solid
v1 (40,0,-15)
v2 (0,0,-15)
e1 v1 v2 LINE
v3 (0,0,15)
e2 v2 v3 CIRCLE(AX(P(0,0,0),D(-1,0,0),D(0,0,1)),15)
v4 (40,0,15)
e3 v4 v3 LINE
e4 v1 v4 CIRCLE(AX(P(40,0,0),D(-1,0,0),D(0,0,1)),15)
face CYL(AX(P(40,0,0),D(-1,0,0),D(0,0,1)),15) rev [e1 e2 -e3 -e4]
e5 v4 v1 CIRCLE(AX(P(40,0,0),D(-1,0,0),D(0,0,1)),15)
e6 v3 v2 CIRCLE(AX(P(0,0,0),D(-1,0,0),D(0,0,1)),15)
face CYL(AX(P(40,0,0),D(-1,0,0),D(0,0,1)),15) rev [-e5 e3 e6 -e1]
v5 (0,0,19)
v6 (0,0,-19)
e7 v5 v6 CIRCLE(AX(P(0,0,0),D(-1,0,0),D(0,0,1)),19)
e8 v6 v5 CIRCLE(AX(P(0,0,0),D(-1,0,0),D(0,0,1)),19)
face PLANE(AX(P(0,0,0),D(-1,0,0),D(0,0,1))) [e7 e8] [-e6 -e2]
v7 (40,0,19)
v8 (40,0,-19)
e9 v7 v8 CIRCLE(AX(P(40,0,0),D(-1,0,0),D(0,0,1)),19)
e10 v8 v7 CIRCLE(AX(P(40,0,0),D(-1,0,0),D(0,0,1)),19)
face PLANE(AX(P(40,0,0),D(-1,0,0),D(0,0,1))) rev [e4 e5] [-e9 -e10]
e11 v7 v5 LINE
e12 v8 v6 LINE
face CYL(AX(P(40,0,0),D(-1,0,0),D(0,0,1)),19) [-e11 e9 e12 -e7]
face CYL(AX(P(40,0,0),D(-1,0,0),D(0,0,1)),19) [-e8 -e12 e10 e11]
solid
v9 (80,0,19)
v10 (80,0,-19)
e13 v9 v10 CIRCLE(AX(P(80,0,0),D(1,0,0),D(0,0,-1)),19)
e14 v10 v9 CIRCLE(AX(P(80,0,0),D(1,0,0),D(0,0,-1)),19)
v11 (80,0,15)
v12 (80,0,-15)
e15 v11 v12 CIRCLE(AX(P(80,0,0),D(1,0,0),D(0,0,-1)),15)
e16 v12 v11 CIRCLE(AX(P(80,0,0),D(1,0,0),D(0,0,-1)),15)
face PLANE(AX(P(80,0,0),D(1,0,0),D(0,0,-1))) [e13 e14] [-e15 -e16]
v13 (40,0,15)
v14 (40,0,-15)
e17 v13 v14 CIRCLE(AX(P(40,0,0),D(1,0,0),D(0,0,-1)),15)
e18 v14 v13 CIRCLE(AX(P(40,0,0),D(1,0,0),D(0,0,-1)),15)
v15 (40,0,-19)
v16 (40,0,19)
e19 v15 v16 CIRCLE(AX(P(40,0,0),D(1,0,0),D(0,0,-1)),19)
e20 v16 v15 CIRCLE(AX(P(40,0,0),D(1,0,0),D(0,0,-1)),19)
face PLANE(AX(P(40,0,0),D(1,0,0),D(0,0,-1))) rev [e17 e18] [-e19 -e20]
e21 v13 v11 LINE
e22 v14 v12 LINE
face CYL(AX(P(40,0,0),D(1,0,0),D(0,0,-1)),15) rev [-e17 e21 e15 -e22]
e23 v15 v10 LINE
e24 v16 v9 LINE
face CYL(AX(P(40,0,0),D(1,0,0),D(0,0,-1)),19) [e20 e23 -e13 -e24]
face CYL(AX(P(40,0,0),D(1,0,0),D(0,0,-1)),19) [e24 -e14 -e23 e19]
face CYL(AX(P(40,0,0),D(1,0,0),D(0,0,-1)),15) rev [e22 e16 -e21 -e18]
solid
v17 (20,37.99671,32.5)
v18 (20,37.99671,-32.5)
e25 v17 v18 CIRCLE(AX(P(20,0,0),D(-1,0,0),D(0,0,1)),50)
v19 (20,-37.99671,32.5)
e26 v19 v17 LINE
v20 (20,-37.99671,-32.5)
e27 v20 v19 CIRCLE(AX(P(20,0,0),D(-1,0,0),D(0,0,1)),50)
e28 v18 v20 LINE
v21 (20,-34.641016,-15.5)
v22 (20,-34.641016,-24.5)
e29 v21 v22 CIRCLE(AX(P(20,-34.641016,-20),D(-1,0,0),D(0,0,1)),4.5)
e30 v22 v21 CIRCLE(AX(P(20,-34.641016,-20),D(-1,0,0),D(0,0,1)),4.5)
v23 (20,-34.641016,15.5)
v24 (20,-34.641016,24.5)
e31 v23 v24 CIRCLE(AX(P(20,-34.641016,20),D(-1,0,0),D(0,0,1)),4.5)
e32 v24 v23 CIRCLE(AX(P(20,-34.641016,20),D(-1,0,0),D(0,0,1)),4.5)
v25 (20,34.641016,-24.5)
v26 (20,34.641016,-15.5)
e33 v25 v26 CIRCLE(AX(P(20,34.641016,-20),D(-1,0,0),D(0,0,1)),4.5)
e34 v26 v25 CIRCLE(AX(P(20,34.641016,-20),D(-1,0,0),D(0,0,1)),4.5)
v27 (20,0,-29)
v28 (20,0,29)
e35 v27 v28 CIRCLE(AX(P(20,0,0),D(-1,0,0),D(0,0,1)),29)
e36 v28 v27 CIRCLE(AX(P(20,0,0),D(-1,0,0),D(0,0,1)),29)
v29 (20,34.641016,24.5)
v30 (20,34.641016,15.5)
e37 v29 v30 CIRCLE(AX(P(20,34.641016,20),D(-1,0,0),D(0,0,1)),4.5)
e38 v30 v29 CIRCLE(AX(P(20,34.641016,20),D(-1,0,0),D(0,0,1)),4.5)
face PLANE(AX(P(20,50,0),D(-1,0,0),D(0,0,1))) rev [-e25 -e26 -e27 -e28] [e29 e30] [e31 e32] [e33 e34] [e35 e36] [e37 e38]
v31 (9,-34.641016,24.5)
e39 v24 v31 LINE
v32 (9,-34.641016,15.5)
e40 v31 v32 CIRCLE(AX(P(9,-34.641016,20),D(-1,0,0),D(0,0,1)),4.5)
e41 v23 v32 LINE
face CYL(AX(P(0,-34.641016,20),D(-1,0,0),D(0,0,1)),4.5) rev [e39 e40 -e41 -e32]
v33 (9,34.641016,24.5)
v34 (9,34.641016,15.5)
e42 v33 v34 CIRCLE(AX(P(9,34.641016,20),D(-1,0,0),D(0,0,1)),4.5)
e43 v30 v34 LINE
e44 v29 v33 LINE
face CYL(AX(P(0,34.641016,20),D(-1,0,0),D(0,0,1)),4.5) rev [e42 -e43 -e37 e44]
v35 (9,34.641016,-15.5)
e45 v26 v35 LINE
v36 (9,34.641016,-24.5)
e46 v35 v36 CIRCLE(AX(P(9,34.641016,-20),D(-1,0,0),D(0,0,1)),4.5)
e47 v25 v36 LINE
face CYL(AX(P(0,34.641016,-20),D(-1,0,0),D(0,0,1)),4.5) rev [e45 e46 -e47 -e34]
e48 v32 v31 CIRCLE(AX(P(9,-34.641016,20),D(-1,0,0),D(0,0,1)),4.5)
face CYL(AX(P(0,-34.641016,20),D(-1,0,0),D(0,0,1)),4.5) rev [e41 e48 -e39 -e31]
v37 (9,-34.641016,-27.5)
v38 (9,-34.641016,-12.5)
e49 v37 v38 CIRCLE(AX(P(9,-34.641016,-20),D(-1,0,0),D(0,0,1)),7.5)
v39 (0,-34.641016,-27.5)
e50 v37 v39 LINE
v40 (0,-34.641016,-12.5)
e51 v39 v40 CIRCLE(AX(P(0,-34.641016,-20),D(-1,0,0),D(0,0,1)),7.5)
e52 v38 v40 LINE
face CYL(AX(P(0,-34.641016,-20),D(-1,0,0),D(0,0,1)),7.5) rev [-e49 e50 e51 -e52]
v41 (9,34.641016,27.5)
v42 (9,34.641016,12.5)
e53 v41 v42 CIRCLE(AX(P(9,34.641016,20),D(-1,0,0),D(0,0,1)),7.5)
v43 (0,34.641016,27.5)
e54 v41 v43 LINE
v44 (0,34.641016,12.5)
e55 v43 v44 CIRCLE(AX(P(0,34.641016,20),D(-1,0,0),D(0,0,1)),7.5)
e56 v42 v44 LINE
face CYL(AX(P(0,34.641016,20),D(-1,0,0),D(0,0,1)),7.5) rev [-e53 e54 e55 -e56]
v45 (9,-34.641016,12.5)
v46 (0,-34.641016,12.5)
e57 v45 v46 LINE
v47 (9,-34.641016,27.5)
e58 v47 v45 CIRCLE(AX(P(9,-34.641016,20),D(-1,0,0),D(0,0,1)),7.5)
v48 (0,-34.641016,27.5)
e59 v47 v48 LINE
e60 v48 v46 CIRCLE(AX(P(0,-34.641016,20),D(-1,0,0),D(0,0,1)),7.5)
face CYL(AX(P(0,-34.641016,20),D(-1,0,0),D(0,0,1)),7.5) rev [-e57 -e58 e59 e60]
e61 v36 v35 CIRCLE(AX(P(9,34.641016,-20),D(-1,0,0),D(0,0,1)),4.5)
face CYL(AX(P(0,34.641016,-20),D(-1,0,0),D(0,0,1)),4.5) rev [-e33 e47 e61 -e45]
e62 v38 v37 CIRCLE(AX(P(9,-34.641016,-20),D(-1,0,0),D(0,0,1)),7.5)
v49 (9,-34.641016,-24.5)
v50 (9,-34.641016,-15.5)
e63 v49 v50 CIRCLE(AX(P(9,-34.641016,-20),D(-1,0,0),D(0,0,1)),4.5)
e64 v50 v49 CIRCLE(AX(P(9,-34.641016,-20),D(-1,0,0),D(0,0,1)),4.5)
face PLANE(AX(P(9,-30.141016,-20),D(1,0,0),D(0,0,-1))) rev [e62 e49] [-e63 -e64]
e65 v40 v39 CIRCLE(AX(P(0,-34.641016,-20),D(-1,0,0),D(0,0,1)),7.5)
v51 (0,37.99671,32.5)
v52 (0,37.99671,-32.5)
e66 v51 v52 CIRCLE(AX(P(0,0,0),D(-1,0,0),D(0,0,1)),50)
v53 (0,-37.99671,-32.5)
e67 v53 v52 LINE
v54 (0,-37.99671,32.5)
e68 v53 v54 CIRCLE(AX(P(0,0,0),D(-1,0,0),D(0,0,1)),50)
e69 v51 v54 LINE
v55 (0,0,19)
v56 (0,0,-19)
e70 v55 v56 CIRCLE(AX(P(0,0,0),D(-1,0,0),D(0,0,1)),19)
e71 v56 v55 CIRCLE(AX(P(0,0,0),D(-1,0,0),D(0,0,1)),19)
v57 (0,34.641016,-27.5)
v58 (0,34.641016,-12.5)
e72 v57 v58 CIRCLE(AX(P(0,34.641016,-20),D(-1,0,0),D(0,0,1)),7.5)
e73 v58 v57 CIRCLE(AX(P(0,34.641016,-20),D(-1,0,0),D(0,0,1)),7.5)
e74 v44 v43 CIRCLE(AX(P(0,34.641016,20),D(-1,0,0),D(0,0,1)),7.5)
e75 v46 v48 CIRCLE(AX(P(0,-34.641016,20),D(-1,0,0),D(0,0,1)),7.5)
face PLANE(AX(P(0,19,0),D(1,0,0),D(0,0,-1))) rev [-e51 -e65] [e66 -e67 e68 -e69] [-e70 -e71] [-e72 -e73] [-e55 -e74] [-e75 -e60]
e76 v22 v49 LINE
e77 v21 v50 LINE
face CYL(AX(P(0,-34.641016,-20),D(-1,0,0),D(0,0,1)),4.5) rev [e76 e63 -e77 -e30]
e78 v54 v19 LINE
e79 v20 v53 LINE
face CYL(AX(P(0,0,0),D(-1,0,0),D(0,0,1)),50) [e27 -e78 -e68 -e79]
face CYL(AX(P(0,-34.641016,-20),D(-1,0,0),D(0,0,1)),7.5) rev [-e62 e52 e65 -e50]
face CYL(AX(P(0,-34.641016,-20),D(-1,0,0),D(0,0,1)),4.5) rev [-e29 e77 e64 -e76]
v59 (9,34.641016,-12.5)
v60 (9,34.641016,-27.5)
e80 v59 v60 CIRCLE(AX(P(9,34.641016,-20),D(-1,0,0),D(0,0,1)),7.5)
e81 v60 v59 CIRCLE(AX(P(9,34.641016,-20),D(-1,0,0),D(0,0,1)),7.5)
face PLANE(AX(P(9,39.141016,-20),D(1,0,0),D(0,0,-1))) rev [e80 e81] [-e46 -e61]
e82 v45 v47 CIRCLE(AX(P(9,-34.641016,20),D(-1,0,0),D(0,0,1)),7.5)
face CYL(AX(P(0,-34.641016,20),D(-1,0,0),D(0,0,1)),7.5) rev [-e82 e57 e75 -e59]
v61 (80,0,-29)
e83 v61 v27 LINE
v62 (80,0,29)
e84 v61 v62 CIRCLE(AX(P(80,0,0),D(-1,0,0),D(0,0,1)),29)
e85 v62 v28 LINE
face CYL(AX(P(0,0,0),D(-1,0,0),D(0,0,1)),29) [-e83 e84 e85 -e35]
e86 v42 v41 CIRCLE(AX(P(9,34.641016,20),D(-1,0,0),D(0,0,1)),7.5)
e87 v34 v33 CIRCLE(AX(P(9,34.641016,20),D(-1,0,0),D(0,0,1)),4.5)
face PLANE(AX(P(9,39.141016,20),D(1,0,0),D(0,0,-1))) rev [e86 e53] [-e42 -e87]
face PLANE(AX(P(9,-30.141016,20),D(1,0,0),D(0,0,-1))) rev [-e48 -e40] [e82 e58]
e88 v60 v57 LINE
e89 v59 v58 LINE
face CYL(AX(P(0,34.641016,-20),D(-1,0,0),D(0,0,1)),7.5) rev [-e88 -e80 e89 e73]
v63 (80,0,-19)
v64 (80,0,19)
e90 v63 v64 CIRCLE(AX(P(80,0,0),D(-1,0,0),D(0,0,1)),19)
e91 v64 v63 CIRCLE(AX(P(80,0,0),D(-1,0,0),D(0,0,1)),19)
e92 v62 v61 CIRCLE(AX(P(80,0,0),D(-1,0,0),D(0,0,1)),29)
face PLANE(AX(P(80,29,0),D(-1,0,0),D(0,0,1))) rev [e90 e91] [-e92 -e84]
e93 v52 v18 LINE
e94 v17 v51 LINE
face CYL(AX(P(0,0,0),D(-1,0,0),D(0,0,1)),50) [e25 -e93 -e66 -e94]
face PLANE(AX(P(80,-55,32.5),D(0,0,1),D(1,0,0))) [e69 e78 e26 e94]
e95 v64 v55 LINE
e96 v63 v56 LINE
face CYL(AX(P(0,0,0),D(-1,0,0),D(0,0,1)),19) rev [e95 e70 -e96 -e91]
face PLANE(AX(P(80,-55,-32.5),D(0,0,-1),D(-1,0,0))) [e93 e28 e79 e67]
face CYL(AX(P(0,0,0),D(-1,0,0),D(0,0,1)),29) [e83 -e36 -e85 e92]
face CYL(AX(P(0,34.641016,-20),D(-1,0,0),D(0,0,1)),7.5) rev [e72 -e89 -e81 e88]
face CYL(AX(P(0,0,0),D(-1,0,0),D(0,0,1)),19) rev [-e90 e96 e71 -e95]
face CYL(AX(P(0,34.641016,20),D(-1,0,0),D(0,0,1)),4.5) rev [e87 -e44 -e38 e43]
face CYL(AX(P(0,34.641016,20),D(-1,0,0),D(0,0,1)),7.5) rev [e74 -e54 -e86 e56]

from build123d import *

# Parameters (mm, degrees)
HOLE_SIZE_PER_SOCKET_HEAD_CAP_SCREW_TYPE_D           = 9
HOLE_SIZE_PER_SOCKET_HEAD_CAP_SCREW_TYPE_CBORE_D     = 15
HOLE_SIZE_PER_SOCKET_HEAD_CAP_SCREW_TYPE_CBORE_DEPTH = 9
SKETCH4_OUTSIDE_W                                    = 134.496
SKETCH4_OUTSIDE_H                                    = 134.496
SKETCH4_OUTSIDE_W_2                                  = 65
SKETCH4_OUTSIDE_H_2                                  = 110
CUT_EXTRUDE1_DEPTH                                   = 107.77078252
SKETCH5_R                                            = 19
SKETCH5_R_2                                          = 15
BOSS_EXTRUDE1_DEPTH                                  = 40
SKETCH6_R                                            = 19
SKETCH6_R_2                                          = 15
BOSS_EXTRUDE2_DEPTH                                  = 40


with BuildPart() as part:
    # Sketch1 → Revolve1 (revolve)
    with BuildSketch(Plane.XY, mode=Mode.PRIVATE) as revolve1_sk:
        Polygon((0, 19), (0, 50), (20, 50), (20, 29), (80, 29), (80, 19), align=None)
    revolve(revolve1_sk.sketch.rotate(Axis((0, 0, 0), (1, 0, 0)), 90), axis=Axis((0, 0, 0), (1, 0, 0)))

    # Hole size per socket head cap screw type1 (through all)
    with Locations(Plane.ZY):
        with Locations((20, 34.641016151), (-20, 34.641016151), (-20, -34.641016151), (20, -34.641016151)):
            CounterBoreHole(HOLE_SIZE_PER_SOCKET_HEAD_CAP_SCREW_TYPE_D / 2, HOLE_SIZE_PER_SOCKET_HEAD_CAP_SCREW_TYPE_CBORE_D / 2, HOLE_SIZE_PER_SOCKET_HEAD_CAP_SCREW_TYPE_CBORE_DEPTH)

    # Sketch4 outside → Cut-Extrude1 (cut, through all)
    with BuildSketch(Plane.ZY):
        Rectangle(SKETCH4_OUTSIDE_W, SKETCH4_OUTSIDE_H)
        Rectangle(SKETCH4_OUTSIDE_W_2, SKETCH4_OUTSIDE_H_2, mode=Mode.SUBTRACT)
    extrude(amount=-CUT_EXTRUDE1_DEPTH, mode=Mode.SUBTRACT)


with BuildPart() as body_2:
    # Sketch5 → Boss-Extrude1 (new body)
    with BuildSketch(Plane(origin=(80, 0, 0), x_dir=(0, 0, -1), z_dir=(1, 0, 0))):
        Circle(SKETCH5_R)
        Circle(SKETCH5_R_2, mode=Mode.SUBTRACT)
    extrude(amount=-BOSS_EXTRUDE1_DEPTH)


with BuildPart() as body_3:
    # Sketch6 → Boss-Extrude2 (new body)
    with BuildSketch(Plane.ZY):
        Circle(SKETCH6_R)
        Circle(SKETCH6_R_2, mode=Mode.SUBTRACT)
    extrude(amount=-BOSS_EXTRUDE2_DEPTH)


solid = Compound([part.part, body_2.part, body_3.part])
